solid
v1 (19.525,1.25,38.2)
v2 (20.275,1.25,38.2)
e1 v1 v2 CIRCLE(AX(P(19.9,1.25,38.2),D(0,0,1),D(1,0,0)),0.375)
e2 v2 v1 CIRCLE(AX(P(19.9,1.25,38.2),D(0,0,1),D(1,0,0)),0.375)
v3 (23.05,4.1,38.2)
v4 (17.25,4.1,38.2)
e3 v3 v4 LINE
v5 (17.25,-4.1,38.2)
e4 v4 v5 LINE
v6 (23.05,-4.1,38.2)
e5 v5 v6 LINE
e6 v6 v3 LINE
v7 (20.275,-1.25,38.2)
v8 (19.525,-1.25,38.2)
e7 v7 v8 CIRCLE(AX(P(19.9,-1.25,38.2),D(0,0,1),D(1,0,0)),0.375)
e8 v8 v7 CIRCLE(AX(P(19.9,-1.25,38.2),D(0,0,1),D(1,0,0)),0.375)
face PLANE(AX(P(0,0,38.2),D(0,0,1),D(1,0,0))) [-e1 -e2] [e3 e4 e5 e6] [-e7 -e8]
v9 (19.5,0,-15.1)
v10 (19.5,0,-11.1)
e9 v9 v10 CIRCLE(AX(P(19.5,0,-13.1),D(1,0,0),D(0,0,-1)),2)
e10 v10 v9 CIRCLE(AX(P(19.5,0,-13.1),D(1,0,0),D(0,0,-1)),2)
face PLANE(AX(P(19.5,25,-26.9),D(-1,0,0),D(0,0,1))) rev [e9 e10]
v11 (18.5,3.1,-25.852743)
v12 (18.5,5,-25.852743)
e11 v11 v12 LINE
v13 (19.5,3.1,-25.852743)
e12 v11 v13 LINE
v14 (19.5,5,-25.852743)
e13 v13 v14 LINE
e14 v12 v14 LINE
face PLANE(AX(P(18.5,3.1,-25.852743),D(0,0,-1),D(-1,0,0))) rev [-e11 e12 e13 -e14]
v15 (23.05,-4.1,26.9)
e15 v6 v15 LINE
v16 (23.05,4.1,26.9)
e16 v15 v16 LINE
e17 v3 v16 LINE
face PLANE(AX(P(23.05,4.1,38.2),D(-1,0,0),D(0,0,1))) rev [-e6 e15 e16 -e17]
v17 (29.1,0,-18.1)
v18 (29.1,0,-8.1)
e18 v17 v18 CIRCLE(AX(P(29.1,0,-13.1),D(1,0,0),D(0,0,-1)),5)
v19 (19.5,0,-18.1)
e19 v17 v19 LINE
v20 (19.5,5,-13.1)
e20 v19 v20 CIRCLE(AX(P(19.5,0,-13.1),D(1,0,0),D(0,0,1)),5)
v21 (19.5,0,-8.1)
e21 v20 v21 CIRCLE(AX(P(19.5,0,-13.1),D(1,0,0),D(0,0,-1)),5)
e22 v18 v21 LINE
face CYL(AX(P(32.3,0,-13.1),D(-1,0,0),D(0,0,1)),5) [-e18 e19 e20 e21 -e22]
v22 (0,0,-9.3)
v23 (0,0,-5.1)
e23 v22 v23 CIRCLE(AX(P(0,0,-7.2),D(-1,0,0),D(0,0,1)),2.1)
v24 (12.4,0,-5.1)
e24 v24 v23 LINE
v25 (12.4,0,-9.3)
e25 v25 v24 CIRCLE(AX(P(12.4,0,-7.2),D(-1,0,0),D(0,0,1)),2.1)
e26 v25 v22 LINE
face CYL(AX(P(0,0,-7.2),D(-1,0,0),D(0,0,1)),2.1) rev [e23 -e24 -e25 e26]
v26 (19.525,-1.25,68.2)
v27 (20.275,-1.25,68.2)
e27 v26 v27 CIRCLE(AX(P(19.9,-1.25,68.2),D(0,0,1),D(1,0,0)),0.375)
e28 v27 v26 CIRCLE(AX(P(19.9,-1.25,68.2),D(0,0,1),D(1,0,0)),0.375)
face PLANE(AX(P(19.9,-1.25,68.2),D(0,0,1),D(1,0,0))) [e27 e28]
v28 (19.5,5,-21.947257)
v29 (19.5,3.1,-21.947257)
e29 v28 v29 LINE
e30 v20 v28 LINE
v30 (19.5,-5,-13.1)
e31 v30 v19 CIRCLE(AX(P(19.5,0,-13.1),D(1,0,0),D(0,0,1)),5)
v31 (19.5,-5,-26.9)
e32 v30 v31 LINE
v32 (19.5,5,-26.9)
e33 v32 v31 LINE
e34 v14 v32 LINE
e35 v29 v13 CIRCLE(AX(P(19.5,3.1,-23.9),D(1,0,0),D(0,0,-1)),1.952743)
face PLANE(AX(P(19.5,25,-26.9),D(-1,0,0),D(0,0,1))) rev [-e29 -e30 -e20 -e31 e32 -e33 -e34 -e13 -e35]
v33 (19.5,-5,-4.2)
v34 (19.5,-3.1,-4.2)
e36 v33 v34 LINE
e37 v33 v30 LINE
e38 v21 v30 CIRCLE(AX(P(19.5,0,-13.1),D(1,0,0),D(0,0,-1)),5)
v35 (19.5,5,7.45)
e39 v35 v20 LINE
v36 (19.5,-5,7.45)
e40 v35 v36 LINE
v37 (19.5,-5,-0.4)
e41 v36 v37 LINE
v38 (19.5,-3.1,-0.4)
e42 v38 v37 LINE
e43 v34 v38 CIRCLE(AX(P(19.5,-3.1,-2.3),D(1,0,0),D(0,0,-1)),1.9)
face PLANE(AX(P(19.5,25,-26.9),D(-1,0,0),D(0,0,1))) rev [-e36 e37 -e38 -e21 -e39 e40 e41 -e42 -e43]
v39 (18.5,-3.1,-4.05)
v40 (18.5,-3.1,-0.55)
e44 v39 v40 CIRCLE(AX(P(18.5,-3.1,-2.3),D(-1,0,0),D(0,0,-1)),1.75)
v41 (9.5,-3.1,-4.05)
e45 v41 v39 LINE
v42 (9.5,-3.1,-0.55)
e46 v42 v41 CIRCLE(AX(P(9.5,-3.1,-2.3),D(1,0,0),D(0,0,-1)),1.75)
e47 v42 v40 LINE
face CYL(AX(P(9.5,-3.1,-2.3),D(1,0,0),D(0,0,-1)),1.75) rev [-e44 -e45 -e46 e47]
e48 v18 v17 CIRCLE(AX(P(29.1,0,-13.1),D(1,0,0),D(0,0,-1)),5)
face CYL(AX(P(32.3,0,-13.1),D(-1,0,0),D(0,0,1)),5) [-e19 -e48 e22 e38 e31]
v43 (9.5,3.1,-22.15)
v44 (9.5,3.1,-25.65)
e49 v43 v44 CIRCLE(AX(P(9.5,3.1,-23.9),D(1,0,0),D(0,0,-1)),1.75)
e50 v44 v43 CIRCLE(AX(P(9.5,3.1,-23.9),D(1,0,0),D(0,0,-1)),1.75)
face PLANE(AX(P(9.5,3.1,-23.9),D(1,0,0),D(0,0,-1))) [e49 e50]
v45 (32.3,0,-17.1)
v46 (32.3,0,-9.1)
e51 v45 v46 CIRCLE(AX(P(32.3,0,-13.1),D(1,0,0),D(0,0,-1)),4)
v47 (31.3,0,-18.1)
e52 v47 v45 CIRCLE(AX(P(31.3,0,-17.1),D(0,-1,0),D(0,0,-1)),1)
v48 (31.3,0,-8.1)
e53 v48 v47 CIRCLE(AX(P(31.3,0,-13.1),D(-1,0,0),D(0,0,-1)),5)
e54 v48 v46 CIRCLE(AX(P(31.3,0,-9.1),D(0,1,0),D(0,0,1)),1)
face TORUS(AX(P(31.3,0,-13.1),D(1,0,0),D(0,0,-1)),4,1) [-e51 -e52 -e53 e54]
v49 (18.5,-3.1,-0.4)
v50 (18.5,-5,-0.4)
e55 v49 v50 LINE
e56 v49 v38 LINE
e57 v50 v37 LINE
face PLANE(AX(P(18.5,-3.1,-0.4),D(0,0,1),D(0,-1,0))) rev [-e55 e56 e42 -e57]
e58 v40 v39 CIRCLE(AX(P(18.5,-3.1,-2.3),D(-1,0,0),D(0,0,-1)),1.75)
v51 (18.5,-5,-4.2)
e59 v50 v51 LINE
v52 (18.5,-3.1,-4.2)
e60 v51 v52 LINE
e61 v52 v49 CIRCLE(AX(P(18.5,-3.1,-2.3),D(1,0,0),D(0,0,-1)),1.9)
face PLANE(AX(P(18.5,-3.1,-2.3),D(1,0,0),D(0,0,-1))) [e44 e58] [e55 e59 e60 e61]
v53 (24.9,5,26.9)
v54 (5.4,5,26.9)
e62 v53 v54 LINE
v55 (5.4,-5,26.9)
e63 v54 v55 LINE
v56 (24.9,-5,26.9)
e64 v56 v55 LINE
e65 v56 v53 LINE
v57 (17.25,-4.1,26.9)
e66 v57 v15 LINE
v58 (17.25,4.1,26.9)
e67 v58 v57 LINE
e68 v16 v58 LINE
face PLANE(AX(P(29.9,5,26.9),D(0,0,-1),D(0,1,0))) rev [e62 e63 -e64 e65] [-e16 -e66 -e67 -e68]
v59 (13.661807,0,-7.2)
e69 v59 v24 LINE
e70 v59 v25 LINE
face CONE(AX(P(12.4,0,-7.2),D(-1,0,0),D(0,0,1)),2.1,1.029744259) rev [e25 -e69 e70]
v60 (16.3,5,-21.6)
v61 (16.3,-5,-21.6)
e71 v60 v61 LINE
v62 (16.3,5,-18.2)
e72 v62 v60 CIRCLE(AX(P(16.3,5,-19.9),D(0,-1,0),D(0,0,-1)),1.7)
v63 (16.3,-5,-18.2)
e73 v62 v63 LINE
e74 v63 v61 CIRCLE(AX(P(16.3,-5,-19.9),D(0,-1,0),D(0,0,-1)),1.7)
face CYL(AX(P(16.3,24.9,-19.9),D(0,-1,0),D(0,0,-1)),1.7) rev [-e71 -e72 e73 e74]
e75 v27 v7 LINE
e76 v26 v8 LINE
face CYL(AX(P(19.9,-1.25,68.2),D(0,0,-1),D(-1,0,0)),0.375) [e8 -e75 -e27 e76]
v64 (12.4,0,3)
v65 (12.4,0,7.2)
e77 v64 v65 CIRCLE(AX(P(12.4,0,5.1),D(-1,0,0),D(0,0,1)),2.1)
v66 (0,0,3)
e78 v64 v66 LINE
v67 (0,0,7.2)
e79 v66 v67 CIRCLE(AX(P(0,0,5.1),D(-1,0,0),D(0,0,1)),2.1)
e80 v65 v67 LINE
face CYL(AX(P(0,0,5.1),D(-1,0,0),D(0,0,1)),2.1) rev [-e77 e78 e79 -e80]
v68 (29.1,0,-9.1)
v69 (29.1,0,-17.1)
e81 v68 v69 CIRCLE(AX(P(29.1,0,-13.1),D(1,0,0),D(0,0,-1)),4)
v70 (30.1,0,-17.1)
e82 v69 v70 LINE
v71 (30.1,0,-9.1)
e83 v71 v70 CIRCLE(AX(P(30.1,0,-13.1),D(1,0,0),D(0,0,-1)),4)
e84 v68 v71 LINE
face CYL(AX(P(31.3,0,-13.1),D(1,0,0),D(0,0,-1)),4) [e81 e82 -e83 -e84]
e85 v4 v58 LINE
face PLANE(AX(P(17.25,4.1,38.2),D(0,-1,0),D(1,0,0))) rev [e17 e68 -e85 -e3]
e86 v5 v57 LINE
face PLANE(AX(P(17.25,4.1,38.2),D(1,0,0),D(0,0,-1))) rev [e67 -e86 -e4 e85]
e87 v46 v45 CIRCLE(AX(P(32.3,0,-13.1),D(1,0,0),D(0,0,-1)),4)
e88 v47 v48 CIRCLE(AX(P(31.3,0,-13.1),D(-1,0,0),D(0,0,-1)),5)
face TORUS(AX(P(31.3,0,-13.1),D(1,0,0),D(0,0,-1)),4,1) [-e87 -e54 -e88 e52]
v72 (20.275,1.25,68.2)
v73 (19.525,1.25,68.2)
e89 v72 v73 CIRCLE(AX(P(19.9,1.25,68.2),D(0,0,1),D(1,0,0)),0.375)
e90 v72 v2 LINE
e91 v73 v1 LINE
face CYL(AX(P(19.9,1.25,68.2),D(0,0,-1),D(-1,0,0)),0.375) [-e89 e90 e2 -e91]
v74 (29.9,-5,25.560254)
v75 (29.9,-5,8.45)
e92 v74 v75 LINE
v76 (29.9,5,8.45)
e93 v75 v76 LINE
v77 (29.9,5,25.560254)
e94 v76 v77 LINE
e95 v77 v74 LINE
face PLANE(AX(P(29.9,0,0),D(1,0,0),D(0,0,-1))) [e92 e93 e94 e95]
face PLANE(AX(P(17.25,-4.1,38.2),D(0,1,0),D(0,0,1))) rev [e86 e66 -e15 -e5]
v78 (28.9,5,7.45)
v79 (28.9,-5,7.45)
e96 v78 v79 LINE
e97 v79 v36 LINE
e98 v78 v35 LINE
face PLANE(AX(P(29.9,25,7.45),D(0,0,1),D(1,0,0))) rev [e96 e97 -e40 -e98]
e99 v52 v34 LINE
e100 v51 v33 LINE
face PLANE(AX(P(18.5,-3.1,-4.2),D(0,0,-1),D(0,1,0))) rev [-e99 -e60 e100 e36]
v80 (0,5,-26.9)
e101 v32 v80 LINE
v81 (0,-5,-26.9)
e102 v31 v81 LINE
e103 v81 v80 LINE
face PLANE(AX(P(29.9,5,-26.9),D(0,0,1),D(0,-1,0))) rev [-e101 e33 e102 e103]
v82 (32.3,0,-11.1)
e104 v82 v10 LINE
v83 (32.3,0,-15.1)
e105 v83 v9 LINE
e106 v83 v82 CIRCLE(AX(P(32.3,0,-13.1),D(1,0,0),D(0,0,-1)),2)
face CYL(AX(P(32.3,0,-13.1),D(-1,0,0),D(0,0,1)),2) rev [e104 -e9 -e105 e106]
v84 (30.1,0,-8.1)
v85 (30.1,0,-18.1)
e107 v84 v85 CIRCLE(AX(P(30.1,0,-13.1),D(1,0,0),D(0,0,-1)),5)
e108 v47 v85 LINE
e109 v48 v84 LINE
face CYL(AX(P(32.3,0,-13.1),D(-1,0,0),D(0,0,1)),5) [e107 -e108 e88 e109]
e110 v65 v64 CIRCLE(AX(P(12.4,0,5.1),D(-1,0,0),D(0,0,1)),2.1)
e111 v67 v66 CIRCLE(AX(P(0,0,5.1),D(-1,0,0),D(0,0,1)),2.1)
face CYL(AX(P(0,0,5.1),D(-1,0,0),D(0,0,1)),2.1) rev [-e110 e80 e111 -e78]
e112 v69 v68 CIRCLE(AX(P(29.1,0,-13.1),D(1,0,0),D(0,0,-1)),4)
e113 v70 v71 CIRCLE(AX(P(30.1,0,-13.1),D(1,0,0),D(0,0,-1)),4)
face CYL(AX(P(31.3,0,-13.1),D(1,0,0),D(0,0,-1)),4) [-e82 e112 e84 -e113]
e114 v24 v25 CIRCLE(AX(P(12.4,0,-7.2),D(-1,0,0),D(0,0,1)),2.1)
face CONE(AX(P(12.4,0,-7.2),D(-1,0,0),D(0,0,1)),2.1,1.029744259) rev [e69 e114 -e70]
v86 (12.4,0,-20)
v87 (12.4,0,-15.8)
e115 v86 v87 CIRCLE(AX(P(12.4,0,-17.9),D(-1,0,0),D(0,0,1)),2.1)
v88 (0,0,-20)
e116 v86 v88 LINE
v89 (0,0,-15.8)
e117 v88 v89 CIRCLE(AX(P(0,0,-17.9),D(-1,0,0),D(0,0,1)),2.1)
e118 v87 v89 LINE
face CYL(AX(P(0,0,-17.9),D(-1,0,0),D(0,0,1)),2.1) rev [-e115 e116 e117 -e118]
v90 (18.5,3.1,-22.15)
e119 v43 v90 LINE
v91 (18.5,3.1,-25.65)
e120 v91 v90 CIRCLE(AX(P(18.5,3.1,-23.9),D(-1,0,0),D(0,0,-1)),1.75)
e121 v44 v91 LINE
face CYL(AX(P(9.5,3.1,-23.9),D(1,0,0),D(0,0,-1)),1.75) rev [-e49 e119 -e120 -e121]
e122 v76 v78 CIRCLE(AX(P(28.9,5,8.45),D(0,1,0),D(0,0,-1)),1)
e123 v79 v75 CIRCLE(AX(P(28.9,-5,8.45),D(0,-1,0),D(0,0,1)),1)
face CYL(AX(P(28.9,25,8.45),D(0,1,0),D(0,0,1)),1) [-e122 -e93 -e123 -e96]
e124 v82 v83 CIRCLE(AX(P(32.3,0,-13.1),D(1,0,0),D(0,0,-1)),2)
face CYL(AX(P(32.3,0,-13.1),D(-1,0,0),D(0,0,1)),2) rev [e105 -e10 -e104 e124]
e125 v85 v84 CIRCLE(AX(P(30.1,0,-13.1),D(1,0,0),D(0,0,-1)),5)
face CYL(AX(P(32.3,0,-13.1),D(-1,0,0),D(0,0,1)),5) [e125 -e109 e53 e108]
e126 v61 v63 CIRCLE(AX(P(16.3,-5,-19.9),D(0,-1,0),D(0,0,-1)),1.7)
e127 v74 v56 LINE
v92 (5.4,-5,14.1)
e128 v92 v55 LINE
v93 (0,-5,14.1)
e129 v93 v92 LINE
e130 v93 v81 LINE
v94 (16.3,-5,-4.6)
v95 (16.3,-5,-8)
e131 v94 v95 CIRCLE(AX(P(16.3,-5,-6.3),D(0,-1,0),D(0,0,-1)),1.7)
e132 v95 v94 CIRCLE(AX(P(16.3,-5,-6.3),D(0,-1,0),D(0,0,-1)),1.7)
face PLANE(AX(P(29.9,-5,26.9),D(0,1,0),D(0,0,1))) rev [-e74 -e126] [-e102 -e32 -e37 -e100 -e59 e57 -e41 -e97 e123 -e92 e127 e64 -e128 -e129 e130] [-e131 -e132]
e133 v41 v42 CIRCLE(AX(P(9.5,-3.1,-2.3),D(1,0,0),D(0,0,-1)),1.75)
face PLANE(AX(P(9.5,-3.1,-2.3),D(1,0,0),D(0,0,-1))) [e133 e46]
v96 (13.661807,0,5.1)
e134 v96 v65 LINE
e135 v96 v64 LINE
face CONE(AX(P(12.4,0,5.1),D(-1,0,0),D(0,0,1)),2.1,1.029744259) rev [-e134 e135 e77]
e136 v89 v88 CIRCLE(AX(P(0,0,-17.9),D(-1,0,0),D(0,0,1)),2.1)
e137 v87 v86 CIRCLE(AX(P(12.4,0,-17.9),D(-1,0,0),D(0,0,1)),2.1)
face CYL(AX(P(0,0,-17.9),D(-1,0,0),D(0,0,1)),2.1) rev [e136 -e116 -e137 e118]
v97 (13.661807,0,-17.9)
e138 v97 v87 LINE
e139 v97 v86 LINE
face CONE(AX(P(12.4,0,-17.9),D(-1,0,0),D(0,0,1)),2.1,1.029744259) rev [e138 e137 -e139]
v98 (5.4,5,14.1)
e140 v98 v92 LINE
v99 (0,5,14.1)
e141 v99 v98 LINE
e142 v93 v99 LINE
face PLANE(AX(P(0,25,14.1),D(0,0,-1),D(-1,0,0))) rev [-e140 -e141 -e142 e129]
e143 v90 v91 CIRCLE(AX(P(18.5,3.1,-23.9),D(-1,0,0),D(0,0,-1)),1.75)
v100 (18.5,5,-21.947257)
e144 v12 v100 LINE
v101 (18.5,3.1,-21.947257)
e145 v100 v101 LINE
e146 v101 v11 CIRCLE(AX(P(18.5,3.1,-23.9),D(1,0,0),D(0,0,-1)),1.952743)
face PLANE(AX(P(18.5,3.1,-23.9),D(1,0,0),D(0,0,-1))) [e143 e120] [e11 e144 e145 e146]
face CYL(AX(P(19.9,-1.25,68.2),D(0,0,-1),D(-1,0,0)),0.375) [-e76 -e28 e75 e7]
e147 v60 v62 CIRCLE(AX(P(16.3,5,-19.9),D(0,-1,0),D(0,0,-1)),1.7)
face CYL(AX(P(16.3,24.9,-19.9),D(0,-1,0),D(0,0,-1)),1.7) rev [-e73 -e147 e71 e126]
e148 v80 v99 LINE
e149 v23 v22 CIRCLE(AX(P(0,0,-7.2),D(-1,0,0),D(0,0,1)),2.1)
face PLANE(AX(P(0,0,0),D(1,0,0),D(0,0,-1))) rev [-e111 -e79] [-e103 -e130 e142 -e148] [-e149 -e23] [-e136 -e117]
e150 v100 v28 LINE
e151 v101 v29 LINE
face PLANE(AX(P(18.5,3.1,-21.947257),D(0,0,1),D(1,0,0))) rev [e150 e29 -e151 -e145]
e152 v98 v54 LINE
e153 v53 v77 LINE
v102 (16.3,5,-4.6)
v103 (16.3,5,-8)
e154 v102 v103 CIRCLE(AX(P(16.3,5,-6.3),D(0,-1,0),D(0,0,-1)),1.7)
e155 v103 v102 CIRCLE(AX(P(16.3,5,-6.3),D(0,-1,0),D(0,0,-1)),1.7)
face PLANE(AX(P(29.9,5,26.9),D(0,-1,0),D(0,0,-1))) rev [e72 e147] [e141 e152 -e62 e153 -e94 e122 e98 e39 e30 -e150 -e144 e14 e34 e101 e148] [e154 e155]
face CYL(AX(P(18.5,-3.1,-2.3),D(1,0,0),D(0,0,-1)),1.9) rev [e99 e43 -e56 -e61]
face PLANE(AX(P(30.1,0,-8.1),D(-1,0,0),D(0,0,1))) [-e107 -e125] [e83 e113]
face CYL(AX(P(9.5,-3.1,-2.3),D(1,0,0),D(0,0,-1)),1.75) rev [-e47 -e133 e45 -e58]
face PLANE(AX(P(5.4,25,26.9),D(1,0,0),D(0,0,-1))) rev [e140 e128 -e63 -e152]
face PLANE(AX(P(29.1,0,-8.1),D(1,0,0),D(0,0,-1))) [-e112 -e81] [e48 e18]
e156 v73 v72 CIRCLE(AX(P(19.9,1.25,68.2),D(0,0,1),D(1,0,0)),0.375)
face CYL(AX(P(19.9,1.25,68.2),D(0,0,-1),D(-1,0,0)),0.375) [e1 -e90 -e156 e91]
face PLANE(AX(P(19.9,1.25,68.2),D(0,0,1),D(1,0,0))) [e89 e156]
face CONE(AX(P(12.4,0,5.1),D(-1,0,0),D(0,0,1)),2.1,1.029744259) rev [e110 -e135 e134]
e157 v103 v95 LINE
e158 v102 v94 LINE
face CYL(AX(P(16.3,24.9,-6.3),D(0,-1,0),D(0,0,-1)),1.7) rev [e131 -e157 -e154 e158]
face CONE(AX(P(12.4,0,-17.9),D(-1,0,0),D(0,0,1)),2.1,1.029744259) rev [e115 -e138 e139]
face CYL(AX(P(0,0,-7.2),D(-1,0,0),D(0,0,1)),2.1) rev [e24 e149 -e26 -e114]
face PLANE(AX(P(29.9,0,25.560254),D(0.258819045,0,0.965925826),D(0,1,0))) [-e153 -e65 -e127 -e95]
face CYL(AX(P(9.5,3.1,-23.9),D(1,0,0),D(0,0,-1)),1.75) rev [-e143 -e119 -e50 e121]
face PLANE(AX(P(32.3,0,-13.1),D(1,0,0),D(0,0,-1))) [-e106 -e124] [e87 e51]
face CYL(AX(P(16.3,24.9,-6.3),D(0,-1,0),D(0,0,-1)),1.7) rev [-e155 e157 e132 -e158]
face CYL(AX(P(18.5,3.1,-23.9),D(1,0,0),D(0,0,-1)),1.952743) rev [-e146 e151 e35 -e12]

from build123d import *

# Parameters (mm, degrees)
SKETCH1_W             = 53.8
SKETCH1_H             = 10
BOSS_EXTRUDE1_DEPTH   = 29.9
SKETCH2_R             = 1.7
CUT_EXTRUDE1_DEPTH    = 29.9
SKETCH5_W             = 5.4
SKETCH5_H             = 12.8
CUT_EXTRUDE3_DEPTH    = 30
M5_TAPPED_HOLE1_D     = 4.2
M5_TAPPED_HOLE1_DEPTH = 12.4
M5_TAPPED_HOLE1_TIP   = 1.2618073
SKETCH3_W             = 5.8
SKETCH3_H             = 8.2
BOSS_EXTRUDE4_DEPTH   = 11.3
SKETCH7_R             = 0.375
BOSS_EXTRUDE5_DEPTH   = 30
SKETCH8_W             = 10.4
SKETCH8_H             = 34.35
CUT_EXTRUDE4_DEPTH    = 30
SKETCH9_R             = 5
SKETCH9_R_2           = 2
BOSS_EXTRUDE6_DEPTH   = 12.8
FILLET1_R             = 1
FILLET2_R             = 1
CHAMFER2_SIZE         = 5
CHAMFER2_SIZE2        = 1.339745962
SKETCH11_W            = 1
SKETCH11_H            = 1
SKETCH12_R            = 1.75
CUT_EXTRUDE5_DEPTH    = 10
CUT_EXTRUDE6_DEPTH    = 1


with BuildPart() as part:
    # Sketch1 → Boss-Extrude1 (new body)
    with BuildSketch(Plane(origin=(0, 0, 0), x_dir=(0, 0, -1), z_dir=(1, 0, 0))):
        Rectangle(SKETCH1_W, SKETCH1_H)
    extrude(amount=BOSS_EXTRUDE1_DEPTH)

    # Sketch2 → Cut-Extrude1 (cut)
    with BuildSketch(Plane.XZ.offset(5)):
        with Locations(Location((16.3, -19.9, 0), (0, 0, 270))):
            Circle(SKETCH2_R)
        with Locations(Location((16.3, -6.3, 0), (0, 0, 270))):
            Circle(SKETCH2_R)
    extrude(amount=-CUT_EXTRUDE1_DEPTH, mode=Mode.SUBTRACT)

    # Sketch5 → Cut-Extrude3 (cut)
    with BuildSketch(Plane.XZ.offset(5)):
        with Locations((2.7, 20.5)):
            Rectangle(SKETCH5_W, SKETCH5_H)
    extrude(amount=-CUT_EXTRUDE3_DEPTH, mode=Mode.SUBTRACT)

    # M5 Tapped Hole1
    with Locations(Plane(origin=(0, 0, -17.9), x_dir=(0, 0, -1), z_dir=(-1, 0, 0))):
        with Locations((0, 0), (-10.7, 0), (-23, 0)):
            Hole(M5_TAPPED_HOLE1_D / 2, depth=M5_TAPPED_HOLE1_DEPTH)
            with Locations((0, 0, -(M5_TAPPED_HOLE1_DEPTH + M5_TAPPED_HOLE1_TIP / 2))):  # 118° drill point
                Cone(0, M5_TAPPED_HOLE1_D / 2, M5_TAPPED_HOLE1_TIP, mode=Mode.SUBTRACT)

    # Sketch3 → Boss-Extrude4 (add)
    with BuildSketch(Plane.XY.offset(26.9)):
        with Locations((20.15, 0)):
            Rectangle(SKETCH3_W, SKETCH3_H)
    extrude(amount=BOSS_EXTRUDE4_DEPTH)

    # Sketch7 → Boss-Extrude5 (add)
    with BuildSketch(Plane.XY.offset(38.2)):
        with Locations((19.9, 1.25)):
            Circle(SKETCH7_R)
        with Locations((19.9, -1.25)):
            Circle(SKETCH7_R)
    extrude(amount=BOSS_EXTRUDE5_DEPTH)

    # Sketch8 → Cut-Extrude4 (cut)
    with BuildSketch(Plane.XZ.offset(5)):
        with Locations((24.7, -9.725)):
            Rectangle(SKETCH8_W, SKETCH8_H)
    extrude(amount=-CUT_EXTRUDE4_DEPTH, mode=Mode.SUBTRACT)

    # Sketch9 → Boss-Extrude6 (add)
    with BuildSketch(Plane(origin=(19.5, 0, 0), x_dir=(0, 0, -1), z_dir=(1, 0, 0))):
        with Locations(Location((13.1, 0, 0), (0, 0, 270))):
            Circle(SKETCH9_R)
        with Locations((13.1, 0)):
            Circle(SKETCH9_R_2, mode=Mode.SUBTRACT)
    extrude(amount=BOSS_EXTRUDE6_DEPTH)

    # Fillet1
    fillet1_edges = [part.edges().sort_by_distance(p)[0] for p in [
        (32.3, 5, -13.1),
    ]]
    fillet(fillet1_edges, radius=FILLET1_R)

    # Fillet2
    fillet2_edges = [part.edges().sort_by_distance(p)[0] for p in [
        (29.9, 0, 7.45),
    ]]
    fillet(fillet2_edges, radius=FILLET2_R)

    # Chamfer2
    chamfer2_edges = [part.edges().sort_by_distance(p)[0] for p in [
        (29.9, 0, 26.9),
    ]]
    chamfer2_side = [part.faces().sort_by_distance(p)[0] for p in [
        (17.047791734, 0, 26.9),
    ]]
    chamfer(chamfer2_edges, length=CHAMFER2_SIZE, length2=CHAMFER2_SIZE2, reference=chamfer2_side[0])

    # Sketch11 → Cut-Revolve1 (revolve, cut)
    with BuildSketch(Plane(origin=(0, 0, 0), x_dir=(1, 0, 0), z_dir=(0, 1, 0)), mode=Mode.PRIVATE) as cut_revolve1_sk:
        with Locations((29.6, 8.6)):
            Rectangle(SKETCH11_W, SKETCH11_H)
    revolve(cut_revolve1_sk.sketch.rotate(Axis((32.3, 0, -13.1), (-1, 0, 0)), 180), axis=Axis((32.3, 0, -13.1), (-1, 0, 0)), mode=Mode.SUBTRACT)

    # Sketch12 → Cut-Extrude5 (cut)
    with BuildSketch(Plane(origin=(19.5, 0, 0), x_dir=(0, 0, -1), z_dir=(1, 0, 0))):
        with Locations((23.9, 3.1)):
            Circle(SKETCH12_R)
        with Locations((2.3, -3.1)):
            Circle(SKETCH12_R)
    extrude(amount=-CUT_EXTRUDE5_DEPTH, mode=Mode.SUBTRACT)

    # Sketch13 → Cut-Extrude6 (cut)
    with BuildSketch(Plane(origin=(19.5, 0, 0), x_dir=(0, 0, -1), z_dir=(1, 0, 0))):
        with BuildLine():
            Line((4.2, -3.1), (4.2, -5))
            Line((4.2, -5), (0.4, -5))
            Line((0.4, -5), (0.4, -3.1))
            ThreePointArc((0.4, -3.1), (2.3, -1.2), (4.2, -3.1))
        make_face()
        with BuildLine():
            Line((25.852743459, 3.1), (25.852743459, 5))
            Line((25.852743459, 5), (21.947256541, 5))
            Line((21.947256541, 5), (21.947256541, 3.1))
            ThreePointArc((21.947256541, 3.1), (23.9, 1.147256541), (25.852743459, 3.1))
        make_face()
    extrude(amount=-CUT_EXTRUDE6_DEPTH, mode=Mode.SUBTRACT)


solid = part.part
